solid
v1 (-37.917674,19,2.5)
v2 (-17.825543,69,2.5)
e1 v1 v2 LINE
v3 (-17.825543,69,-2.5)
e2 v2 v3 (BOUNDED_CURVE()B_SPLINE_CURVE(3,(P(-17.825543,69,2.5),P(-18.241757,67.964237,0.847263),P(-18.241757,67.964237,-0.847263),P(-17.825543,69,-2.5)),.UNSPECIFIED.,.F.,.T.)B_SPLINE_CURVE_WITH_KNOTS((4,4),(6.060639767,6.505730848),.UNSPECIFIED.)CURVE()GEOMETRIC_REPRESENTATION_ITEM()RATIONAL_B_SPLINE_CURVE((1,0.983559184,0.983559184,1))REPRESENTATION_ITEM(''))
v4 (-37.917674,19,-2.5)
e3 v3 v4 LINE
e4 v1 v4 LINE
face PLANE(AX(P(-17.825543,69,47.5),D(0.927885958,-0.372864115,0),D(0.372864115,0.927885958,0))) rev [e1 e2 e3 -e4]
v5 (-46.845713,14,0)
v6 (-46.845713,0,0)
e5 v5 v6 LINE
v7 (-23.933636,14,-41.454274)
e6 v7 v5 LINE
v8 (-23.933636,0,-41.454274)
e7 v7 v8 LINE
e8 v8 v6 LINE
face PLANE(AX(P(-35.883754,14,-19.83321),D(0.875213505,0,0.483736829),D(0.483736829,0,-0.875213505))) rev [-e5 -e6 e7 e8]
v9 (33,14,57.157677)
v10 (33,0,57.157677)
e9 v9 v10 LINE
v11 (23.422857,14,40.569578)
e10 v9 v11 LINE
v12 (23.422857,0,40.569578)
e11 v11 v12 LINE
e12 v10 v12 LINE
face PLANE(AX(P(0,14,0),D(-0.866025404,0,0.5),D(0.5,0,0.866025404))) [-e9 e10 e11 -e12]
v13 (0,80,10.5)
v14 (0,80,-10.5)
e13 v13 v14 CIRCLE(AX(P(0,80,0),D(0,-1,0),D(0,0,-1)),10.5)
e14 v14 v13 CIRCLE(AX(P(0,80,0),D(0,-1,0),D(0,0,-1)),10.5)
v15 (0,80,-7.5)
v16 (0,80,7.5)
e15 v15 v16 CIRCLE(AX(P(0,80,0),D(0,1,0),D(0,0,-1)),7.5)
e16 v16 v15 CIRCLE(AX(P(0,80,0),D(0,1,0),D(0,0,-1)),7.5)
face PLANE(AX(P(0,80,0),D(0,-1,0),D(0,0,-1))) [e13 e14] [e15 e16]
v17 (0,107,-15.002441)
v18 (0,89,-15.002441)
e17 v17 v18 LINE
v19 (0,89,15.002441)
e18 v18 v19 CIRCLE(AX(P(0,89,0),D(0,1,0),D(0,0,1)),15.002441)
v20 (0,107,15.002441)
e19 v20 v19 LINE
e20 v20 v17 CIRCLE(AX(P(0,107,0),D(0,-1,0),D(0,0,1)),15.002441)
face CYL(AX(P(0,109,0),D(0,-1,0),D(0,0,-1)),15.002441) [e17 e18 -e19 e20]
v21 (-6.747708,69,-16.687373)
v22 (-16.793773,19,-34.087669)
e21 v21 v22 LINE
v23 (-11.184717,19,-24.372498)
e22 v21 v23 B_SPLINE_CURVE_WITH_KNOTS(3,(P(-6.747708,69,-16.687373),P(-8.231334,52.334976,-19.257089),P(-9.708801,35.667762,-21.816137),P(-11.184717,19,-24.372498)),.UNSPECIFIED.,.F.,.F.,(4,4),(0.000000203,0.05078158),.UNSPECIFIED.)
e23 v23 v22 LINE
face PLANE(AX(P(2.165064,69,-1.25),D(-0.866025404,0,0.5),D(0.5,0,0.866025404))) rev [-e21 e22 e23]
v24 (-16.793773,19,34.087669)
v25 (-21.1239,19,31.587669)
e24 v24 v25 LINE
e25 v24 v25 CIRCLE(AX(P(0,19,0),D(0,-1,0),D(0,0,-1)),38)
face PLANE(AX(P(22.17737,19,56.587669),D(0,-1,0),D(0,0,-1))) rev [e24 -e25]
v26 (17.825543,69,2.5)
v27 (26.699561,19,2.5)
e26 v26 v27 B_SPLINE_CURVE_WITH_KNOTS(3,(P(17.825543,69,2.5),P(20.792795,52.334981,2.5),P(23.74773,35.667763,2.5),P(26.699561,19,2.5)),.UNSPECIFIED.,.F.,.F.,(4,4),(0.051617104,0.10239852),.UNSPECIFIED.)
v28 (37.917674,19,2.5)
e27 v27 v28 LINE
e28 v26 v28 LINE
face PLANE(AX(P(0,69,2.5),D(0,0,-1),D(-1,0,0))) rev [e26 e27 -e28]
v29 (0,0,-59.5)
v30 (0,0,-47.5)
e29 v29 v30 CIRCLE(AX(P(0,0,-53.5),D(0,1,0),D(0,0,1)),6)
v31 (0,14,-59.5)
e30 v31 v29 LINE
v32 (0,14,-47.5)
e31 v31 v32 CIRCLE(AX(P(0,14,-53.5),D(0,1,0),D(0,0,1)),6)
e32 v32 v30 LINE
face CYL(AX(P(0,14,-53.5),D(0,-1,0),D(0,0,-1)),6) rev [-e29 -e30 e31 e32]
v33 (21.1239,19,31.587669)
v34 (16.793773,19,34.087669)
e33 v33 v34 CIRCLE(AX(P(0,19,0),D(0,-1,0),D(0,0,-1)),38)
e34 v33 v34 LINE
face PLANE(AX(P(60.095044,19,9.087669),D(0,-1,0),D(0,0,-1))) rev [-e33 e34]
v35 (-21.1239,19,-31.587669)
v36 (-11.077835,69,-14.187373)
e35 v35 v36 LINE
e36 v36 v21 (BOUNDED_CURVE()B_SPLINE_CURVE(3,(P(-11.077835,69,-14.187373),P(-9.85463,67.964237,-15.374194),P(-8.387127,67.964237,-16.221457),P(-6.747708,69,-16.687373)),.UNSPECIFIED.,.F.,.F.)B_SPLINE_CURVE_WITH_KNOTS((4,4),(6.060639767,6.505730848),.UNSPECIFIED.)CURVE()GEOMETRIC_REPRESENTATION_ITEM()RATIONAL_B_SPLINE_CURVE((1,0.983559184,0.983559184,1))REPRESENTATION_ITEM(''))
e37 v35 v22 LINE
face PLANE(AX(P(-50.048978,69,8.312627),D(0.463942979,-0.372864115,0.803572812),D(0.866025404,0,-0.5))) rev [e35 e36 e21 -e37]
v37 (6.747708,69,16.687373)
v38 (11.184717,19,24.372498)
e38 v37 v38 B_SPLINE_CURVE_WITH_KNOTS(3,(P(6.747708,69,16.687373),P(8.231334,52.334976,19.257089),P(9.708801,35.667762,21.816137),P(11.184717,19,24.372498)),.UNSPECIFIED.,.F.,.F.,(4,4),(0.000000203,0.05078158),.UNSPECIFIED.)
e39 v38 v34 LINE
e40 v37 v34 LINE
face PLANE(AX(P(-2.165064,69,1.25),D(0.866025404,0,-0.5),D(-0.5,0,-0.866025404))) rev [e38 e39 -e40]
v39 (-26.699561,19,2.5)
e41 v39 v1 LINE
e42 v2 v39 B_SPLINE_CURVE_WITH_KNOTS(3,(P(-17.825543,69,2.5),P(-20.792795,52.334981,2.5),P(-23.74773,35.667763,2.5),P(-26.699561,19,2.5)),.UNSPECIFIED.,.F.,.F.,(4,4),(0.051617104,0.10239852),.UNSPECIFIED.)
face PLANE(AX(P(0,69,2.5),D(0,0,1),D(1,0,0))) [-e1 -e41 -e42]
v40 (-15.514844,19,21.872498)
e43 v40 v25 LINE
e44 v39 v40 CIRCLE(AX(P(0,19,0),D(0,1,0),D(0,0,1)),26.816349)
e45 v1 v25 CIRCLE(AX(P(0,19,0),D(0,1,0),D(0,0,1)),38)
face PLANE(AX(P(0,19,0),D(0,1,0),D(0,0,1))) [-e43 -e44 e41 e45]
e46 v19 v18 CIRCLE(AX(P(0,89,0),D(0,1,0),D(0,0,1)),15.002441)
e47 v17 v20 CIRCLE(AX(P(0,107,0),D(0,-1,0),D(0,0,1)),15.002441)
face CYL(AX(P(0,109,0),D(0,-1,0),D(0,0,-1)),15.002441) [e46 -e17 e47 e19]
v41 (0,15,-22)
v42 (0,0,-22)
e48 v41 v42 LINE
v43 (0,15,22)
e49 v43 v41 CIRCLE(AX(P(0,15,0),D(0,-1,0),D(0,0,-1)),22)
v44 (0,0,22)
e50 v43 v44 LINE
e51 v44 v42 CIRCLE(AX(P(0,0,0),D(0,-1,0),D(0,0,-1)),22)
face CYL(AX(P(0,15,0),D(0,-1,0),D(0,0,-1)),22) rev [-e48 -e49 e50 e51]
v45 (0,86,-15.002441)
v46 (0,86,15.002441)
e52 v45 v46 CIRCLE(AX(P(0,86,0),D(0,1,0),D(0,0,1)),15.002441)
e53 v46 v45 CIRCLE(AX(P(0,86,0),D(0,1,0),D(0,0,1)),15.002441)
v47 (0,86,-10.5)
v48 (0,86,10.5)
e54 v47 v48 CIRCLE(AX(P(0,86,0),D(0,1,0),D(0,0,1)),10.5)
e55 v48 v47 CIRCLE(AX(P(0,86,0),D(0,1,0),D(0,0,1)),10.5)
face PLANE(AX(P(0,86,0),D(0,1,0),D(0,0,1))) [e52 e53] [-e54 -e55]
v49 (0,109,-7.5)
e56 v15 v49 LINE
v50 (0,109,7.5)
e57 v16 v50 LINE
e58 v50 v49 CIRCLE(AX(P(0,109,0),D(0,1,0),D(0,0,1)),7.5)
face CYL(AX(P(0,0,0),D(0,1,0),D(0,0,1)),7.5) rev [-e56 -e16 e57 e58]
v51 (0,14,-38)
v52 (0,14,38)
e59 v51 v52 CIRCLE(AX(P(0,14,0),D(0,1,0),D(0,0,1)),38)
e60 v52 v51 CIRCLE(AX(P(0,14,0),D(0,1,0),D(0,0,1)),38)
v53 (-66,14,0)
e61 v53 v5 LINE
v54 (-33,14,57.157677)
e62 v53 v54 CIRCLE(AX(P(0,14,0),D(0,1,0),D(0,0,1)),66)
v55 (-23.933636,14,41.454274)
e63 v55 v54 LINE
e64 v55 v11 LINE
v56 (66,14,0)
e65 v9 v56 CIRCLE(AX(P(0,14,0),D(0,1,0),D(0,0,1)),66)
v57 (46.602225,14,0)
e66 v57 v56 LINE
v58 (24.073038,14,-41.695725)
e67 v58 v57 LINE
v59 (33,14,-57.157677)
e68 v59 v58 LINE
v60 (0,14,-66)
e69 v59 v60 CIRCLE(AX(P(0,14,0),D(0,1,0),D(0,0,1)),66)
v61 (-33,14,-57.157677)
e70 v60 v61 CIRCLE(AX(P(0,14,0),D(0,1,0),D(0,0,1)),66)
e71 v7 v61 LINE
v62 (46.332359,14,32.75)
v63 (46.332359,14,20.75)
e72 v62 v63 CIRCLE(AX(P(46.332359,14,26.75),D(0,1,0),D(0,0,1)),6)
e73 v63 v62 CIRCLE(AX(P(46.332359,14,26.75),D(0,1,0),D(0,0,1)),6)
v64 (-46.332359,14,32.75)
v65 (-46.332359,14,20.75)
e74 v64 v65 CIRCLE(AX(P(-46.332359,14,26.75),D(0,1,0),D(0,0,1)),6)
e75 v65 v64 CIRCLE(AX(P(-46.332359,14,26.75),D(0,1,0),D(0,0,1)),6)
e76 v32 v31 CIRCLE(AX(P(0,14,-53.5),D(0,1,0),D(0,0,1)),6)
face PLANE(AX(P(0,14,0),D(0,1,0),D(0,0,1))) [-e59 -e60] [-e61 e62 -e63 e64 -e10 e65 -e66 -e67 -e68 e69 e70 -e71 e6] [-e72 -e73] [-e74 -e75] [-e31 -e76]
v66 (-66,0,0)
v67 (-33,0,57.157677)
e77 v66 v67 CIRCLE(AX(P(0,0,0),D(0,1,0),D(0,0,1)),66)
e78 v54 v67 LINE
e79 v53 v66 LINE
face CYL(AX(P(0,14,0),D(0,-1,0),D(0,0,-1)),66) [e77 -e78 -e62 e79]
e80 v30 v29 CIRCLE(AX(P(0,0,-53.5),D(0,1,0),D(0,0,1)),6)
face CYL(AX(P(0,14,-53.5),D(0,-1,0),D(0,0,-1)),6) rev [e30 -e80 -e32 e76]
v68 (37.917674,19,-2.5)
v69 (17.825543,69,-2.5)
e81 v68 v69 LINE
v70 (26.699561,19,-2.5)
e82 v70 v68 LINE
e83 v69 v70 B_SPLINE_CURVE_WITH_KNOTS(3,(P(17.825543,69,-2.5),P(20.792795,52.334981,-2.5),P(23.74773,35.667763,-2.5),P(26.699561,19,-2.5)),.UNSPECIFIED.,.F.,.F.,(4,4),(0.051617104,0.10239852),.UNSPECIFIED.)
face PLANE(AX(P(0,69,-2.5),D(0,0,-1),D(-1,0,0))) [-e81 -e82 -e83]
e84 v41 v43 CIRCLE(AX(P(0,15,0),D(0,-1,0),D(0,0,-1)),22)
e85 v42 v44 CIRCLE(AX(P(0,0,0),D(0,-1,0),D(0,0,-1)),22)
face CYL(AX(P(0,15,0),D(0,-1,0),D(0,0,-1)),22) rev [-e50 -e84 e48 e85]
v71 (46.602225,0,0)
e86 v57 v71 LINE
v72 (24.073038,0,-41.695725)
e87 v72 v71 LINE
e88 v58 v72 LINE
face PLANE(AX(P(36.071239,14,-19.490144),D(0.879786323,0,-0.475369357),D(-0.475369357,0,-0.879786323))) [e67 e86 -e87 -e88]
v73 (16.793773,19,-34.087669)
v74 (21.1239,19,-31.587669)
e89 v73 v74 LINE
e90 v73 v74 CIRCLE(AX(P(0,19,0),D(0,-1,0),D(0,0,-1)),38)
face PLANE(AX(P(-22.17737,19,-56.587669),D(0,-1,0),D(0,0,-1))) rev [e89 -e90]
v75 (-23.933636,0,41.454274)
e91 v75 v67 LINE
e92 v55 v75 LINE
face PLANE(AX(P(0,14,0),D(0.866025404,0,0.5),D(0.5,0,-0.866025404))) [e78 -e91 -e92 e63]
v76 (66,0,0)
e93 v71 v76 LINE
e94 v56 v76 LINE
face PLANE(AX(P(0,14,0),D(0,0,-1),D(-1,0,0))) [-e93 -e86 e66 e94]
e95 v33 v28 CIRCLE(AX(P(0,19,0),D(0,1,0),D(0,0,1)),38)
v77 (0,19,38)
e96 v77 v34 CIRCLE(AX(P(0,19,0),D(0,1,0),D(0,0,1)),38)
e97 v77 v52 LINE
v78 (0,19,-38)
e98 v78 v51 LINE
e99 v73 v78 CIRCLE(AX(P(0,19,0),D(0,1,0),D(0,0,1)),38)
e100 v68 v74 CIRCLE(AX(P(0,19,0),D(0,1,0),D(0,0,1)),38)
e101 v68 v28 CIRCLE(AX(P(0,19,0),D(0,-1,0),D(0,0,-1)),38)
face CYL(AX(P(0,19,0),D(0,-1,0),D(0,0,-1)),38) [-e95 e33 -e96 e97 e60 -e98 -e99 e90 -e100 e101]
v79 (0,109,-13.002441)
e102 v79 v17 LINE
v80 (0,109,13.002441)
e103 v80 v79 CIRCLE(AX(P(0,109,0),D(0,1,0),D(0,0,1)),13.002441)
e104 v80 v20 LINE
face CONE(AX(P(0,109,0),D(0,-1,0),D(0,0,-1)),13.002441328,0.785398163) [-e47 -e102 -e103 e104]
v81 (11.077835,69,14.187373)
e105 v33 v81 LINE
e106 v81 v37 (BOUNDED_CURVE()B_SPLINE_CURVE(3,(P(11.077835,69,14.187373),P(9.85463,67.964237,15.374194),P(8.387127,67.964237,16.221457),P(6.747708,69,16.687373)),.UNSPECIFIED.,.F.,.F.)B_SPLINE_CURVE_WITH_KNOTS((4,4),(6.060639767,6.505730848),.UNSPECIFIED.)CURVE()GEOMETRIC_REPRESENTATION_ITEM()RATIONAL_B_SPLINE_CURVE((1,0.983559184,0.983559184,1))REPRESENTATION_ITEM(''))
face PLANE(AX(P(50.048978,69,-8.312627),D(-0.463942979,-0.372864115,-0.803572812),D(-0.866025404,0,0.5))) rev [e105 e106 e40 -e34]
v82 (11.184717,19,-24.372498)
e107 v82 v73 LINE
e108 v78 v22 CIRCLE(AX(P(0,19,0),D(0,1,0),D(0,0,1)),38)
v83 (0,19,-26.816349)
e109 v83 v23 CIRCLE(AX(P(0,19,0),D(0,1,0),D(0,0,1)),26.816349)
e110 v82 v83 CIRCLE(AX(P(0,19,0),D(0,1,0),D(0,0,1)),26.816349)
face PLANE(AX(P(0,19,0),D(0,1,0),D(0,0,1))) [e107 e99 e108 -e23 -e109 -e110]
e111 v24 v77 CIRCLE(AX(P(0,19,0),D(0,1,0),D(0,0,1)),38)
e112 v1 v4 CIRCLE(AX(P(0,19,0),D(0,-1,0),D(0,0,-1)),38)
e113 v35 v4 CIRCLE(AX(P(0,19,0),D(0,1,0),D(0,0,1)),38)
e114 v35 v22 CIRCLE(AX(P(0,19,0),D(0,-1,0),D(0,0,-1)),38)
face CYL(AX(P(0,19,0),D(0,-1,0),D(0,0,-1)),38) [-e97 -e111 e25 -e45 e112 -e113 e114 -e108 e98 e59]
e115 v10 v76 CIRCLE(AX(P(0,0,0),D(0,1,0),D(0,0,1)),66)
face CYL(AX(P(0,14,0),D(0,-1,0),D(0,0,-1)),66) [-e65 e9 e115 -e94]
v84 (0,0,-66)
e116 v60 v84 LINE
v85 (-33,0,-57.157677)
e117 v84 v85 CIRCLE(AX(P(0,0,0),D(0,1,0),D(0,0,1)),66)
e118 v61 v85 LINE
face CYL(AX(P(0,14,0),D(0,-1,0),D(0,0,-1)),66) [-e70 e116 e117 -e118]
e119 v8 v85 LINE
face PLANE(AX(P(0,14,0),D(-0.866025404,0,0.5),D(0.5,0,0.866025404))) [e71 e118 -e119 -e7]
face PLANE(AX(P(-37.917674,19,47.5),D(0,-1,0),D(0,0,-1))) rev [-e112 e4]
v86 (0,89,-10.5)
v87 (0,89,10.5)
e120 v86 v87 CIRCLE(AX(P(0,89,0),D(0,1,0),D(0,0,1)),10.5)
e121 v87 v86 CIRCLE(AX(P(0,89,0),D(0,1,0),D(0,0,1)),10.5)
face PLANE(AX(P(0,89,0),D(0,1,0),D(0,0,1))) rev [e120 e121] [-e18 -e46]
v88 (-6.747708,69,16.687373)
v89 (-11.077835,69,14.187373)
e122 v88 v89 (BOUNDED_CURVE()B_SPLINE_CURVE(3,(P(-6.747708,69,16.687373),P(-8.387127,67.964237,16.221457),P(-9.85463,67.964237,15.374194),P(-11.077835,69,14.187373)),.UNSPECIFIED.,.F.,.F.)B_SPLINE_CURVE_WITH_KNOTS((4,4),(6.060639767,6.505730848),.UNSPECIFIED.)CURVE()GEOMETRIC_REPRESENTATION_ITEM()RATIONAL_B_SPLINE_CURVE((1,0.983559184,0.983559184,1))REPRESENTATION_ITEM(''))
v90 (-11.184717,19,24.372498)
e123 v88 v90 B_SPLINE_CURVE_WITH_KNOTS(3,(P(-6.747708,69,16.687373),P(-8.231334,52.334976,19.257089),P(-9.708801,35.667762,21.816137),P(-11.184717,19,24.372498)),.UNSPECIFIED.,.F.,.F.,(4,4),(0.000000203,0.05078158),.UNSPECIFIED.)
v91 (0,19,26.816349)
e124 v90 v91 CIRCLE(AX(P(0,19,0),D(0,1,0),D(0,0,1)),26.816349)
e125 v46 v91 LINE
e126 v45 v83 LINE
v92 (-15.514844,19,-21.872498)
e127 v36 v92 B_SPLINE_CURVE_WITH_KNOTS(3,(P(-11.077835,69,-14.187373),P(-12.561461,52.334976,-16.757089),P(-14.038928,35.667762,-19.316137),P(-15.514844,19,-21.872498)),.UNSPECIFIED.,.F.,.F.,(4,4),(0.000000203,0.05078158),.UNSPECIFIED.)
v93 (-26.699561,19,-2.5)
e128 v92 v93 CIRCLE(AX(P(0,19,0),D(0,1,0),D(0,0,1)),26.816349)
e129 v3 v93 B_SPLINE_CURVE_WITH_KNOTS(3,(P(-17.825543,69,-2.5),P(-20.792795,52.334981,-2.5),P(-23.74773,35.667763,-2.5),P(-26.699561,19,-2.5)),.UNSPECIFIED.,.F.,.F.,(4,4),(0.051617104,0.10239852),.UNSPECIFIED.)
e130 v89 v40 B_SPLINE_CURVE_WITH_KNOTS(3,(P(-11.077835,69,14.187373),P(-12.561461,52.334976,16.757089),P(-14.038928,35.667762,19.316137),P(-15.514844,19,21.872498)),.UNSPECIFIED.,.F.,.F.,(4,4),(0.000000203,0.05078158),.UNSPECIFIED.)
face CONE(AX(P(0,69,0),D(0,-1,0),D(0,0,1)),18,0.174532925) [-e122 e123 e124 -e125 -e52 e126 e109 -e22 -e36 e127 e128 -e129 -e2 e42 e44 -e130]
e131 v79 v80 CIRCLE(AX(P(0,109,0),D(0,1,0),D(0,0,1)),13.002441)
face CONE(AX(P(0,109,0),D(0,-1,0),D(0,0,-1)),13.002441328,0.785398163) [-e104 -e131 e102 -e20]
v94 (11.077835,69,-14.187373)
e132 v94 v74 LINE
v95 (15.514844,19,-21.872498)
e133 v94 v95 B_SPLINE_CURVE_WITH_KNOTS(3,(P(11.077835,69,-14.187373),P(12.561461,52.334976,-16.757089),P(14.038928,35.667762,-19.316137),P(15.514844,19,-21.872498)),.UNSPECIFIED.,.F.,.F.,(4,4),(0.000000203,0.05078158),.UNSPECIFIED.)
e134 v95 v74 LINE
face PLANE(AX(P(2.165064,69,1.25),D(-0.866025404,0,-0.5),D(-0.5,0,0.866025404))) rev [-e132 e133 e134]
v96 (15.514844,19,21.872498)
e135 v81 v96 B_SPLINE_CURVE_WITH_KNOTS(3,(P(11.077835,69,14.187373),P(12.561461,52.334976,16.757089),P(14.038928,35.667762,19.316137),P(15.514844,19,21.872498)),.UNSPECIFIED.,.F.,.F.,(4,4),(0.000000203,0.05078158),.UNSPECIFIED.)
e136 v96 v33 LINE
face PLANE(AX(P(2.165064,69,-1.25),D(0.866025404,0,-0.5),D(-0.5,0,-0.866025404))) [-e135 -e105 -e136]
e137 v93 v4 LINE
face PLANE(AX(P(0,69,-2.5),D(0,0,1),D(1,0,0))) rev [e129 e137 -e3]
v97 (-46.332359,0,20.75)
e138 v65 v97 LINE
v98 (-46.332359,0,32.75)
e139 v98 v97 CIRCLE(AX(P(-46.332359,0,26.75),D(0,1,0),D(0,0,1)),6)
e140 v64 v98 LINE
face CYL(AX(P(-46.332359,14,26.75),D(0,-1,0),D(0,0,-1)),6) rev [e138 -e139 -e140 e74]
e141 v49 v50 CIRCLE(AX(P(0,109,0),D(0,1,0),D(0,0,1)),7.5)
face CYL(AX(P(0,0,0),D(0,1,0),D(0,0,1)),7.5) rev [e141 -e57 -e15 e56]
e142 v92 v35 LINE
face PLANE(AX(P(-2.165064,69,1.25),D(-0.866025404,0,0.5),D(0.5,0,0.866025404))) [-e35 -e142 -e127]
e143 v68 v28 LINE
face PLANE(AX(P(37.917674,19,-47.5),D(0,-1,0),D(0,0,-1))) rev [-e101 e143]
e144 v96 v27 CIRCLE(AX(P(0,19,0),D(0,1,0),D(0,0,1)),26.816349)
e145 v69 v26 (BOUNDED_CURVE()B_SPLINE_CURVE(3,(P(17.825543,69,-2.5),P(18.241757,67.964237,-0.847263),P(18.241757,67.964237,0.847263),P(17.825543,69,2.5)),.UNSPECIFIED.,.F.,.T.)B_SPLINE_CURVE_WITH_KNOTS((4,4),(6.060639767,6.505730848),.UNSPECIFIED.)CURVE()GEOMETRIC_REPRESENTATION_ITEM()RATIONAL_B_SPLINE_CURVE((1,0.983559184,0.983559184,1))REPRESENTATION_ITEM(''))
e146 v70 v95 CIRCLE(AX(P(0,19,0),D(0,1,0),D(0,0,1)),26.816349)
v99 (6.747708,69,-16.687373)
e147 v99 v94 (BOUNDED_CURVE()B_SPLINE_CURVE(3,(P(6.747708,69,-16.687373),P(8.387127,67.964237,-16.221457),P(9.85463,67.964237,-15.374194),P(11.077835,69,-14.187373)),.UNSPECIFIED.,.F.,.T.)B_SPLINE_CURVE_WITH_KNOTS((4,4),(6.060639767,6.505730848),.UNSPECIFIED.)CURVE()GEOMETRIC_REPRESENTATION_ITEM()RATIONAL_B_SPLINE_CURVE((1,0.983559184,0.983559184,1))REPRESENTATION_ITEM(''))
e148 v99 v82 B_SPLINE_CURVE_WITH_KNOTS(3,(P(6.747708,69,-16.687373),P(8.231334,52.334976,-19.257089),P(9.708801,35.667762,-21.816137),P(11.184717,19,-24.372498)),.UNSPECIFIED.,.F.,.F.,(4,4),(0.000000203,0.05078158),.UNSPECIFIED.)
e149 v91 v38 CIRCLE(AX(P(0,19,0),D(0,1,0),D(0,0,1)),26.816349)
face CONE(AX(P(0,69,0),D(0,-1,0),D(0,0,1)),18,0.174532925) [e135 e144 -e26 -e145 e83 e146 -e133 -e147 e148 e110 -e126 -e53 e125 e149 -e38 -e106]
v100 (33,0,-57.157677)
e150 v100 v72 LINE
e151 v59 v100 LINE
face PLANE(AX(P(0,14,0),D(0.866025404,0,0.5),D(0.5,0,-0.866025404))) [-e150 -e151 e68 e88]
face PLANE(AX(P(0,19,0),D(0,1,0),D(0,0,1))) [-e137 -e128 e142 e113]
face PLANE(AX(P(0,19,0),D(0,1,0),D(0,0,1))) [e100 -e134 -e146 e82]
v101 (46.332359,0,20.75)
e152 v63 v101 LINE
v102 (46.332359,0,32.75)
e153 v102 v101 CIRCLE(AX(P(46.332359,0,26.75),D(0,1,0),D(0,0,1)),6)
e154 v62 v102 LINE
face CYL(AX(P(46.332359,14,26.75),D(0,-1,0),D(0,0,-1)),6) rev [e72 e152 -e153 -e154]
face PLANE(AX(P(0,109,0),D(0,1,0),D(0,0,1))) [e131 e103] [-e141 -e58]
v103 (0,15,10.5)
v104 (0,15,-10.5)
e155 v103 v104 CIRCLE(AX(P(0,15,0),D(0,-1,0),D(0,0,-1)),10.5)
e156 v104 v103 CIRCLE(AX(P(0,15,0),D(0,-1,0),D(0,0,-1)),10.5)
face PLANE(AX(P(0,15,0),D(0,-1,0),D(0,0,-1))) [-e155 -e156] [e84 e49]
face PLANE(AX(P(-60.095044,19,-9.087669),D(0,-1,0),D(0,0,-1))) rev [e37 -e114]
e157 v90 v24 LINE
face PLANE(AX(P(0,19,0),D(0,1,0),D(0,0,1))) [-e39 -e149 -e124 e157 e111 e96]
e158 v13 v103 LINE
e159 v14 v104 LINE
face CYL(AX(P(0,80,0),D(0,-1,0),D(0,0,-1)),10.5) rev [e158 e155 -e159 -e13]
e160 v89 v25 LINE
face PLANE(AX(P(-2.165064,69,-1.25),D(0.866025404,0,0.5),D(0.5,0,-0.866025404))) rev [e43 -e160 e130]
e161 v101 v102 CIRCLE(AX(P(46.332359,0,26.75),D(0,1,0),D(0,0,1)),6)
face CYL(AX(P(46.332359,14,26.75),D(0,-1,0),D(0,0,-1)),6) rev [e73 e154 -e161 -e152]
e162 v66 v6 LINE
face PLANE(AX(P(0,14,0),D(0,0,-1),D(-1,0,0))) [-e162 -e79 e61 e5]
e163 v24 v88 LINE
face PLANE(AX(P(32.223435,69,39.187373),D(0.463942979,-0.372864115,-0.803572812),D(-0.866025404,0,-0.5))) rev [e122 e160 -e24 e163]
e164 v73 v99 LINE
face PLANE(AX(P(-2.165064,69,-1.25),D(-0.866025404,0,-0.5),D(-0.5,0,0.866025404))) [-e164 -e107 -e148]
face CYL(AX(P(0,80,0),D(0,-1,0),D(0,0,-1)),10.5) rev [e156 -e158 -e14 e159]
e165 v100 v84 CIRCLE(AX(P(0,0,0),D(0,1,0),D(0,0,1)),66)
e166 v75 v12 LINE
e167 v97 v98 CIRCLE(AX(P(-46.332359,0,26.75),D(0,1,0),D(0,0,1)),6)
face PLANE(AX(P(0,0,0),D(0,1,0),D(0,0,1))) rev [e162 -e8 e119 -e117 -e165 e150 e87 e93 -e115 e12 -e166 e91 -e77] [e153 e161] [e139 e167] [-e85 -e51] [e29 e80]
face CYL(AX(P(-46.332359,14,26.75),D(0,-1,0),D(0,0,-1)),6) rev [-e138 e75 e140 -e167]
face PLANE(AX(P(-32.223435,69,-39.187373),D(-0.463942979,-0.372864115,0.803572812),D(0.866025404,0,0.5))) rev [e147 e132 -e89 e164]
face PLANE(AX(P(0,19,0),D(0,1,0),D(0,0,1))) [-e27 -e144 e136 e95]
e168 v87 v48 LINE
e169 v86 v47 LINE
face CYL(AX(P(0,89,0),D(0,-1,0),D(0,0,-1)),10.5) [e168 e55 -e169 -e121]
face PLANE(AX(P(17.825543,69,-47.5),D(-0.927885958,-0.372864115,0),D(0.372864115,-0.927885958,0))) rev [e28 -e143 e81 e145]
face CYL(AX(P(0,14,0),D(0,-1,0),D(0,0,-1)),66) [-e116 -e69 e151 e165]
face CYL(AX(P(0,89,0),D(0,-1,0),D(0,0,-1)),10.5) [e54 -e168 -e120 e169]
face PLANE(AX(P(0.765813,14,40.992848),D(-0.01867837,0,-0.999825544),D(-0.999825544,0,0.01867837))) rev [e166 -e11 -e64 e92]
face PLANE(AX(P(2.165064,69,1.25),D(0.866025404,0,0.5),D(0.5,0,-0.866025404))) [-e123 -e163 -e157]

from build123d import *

# Parameters (mm, degrees)
BASE_FLANGE_SKETCH_R             = 6
F_3_LOBE_BASE_FLANGE_DEPTH       = 14
LOCATING_COLLAR_SKETCH_R         = 38
LOCATING_COLLAR_76_DEPTH         = 5
RIB_WEB_DEPTH                    = 50
RIB_SLOT_CUT_1_DEPTH             = 50
RIB_SLOT_CUT_2_DEPTH             = 50
RIB_SLOT_CUT_3_DEPTH             = 50
RIB_SLOT_CUT_4_DEPTH             = 50
RIB_SLOT_CUT_5_DEPTH             = 50
RIB_SLOT_CUT_6_DEPTH             = 50
CONE_BASE_SKETCH_36_R            = 18
CONICAL_COLUMN_10DEG_DRAFT_DEPTH = 17
CONICAL_COLUMN_10DEG_DRAFT_TAPER = 10
SKETCH10_2_R                     = 18
CONE_CORE_THROUGH_RIBS_DEPTH     = 50
CONE_CORE_THROUGH_RIBS_DRAFT     = 10
NECK_SKETCH_R                    = 10.5
NECK_21_DEPTH                    = 3
TOP_SPIGOT_SKETCH_R              = 15.002441328
TOP_SPIGOT_30_DEPTH              = 20
SPIGOT_CHAMFER_2MM_SIZE          = 2
THROUGH_BORE_SKETCH_R            = 7.5
THROUGH_BORE_15_DEPTH            = 144.502613217
UNDERSIDE_COUNTERBORE_SKETCH_R   = 22
UNDERSIDE_COUNTERBORE_44_DEPTH   = 15
INNER_BORE_SKETCH_R              = 10.5
INNER_BORE_21_DEPTH              = 65


with BuildPart() as part:
    # Base Flange Sketch → 3-Lobe Base Flange (new body)
    with BuildSketch(Plane(origin=(0, 0, 0), x_dir=(1, 0, 0), z_dir=(0, 1, 0))):
        with BuildLine():
            Line((33, -57.15767665), (23.422856537, -40.56957758))
            Line((23.422856537, -40.56957758), (-23.933636252, -41.454273999))
            Line((-23.933636252, -41.454273999), (-33, -57.15767665))
            ThreePointArc((-33, -57.15767665), (-57.15767665, -33), (-66, 0))
            Line((-66, 0), (-46.845713073, 0))
            Line((-46.845713073, 0), (-23.933636252, 41.454273999))
            Line((-23.933636252, 41.454273999), (-33, 57.15767665))
            ThreePointArc((-33, 57.15767665), (0, 66), (33, 57.15767665))
            Line((33, 57.15767665), (24.073038277, 41.695725388))
            Line((24.073038277, 41.695725388), (46.60222479, 0))
            Line((46.60222479, 0), (66, 0))
            ThreePointArc((66, 0), (57.15767665, -33), (33, -57.15767665))
        make_face()
        with Locations(Location((0, 53.5, 0), (0, 0, 270))):
            Circle(BASE_FLANGE_SKETCH_R, mode=Mode.SUBTRACT)
        with Locations(Location((46.332359102, -26.75, 0), (0, 0, 270))):
            Circle(BASE_FLANGE_SKETCH_R, mode=Mode.SUBTRACT)
        with Locations(Location((-46.332359102, -26.75, 0), (0, 0, 270))):
            Circle(BASE_FLANGE_SKETCH_R, mode=Mode.SUBTRACT)
    extrude(amount=F_3_LOBE_BASE_FLANGE_DEPTH)

    # Locating Collar Sketch → Locating Collar _76 (add)
    with BuildSketch(Plane(origin=(0, 14, 0), x_dir=(1, 0, 0), z_dir=(0, 1, 0))):
        with Locations(Location((0, 0, 0), (0, 0, 270))):
            Circle(LOCATING_COLLAR_SKETCH_R)
    extrude(amount=LOCATING_COLLAR_76_DEPTH)

    # Rib Web Sketch → Rib Web (add)
    with BuildSketch(Plane(origin=(0, 19, 0), x_dir=(1, 0, 0), z_dir=(0, 1, 0))):
        with BuildLine():
            Line((37.917673979, 2.5), (17.82554347, 2.5))
            ThreePointArc((17.82554347, 2.5), (15.588457268, 9), (11.077835244, 14.187373481))
            Line((11.077835244, 14.187373481), (21.123900499, 31.587668918))
            ThreePointArc((21.123900499, 31.587668918), (19, 32.908965344), (16.79377348, 34.087668918))
            Line((16.79377348, 34.087668918), (6.747708226, 16.687373481))
            ThreePointArc((6.747708226, 16.687373481), (0, 18), (-6.747708226, 16.687373481))
            Line((-6.747708226, 16.687373481), (-16.79377348, 34.087668918))
            ThreePointArc((-16.79377348, 34.087668918), (-19, 32.908965344), (-21.123900499, 31.587668918))
            Line((-21.123900499, 31.587668918), (-11.077835244, 14.187373481))
            ThreePointArc((-11.077835244, 14.187373481), (-15.588457268, 9), (-17.82554347, 2.5))
            Line((-17.82554347, 2.5), (-37.917673979, 2.5))
            ThreePointArc((-37.917673979, 2.5), (-38, 0), (-37.917673979, -2.5))
            Line((-37.917673979, -2.5), (-17.82554347, -2.5))
            ThreePointArc((-17.82554347, -2.5), (-15.588457268, -9), (-11.077835244, -14.187373481))
            Line((-11.077835244, -14.187373481), (-21.123900499, -31.587668918))
            ThreePointArc((-21.123900499, -31.587668918), (-19, -32.908965344), (-16.79377348, -34.087668918))
            Line((-16.79377348, -34.087668918), (-6.747708226, -16.687373481))
            ThreePointArc((-6.747708226, -16.687373481), (0, -18), (6.747708226, -16.687373481))
            Line((6.747708226, -16.687373481), (16.79377348, -34.087668918))
            ThreePointArc((16.79377348, -34.087668918), (19, -32.908965344), (21.123900499, -31.587668918))
            Line((21.123900499, -31.587668918), (11.077835244, -14.187373481))
            ThreePointArc((11.077835244, -14.187373481), (15.588457268, -9), (17.82554347, -2.5))
            Line((17.82554347, -2.5), (37.917673979, -2.5))
            ThreePointArc((37.917673979, -2.5), (37.979412918, -1.250677574), (38, 0))
            ThreePointArc((38, 0), (37.979412918, 1.250677574), (37.917673979, 2.5))
        make_face()
    extrude(amount=RIB_WEB_DEPTH)

    # Rib Slot 1 Sketch → Rib Slot Cut 1 (cut)
    with BuildSketch(Plane(origin=(-2.165063509, 0, 1.25), x_dir=(0.5000000000000031, 0, 0.8660254037844369), z_dir=(-0.8660254037844369, 0, 0.5000000000000031))):
        Polygon((17.82554347, 69), (37.917673979, 19), (44.908281954, 19), (44.908281954, 71.637843916), align=None)
    extrude(amount=-RIB_SLOT_CUT_1_DEPTH, mode=Mode.SUBTRACT)

    # Rib Slot 2 Sketch → Rib Slot Cut 2 (cut)
    with BuildSketch(Plane.XY.offset(2.5)):
        Polygon((37.917673979, 19), (41.484682242, 19), (43.003646089, 71.350074734), (17.82554347, 69), align=None)
    extrude(amount=-RIB_SLOT_CUT_2_DEPTH, mode=Mode.SUBTRACT)

    # Rib Slot 3 Sketch → Rib Slot Cut 3 (cut)
    with BuildSketch(Plane(origin=(2.165063509, 0, 1.25), x_dir=(0.49999999999999784, 0, -0.86602540378444), z_dir=(0.86602540378444, 0, 0.49999999999999784))):
        Polygon((17.82554347, 69), (37.917673979, 19), (41.057228015, 19), (41.057228015, 71.20053138), align=None)
    extrude(amount=-RIB_SLOT_CUT_3_DEPTH, mode=Mode.SUBTRACT)

    # Rib Slot 4 Sketch → Rib Slot Cut 4 (cut)
    with BuildSketch(Plane(origin=(2.165063509, 0, -1.25), x_dir=(-0.5000000000000029, 0, -0.866025403784437), z_dir=(0.866025403784437, 0, -0.5000000000000029))):
        Polygon((17.82554347, 69), (37.917673979, 19), (43.490166386, 19), (43.490166386, 73.364655625), align=None)
    extrude(amount=-RIB_SLOT_CUT_4_DEPTH, mode=Mode.SUBTRACT)

    # Rib Slot 5 Sketch → Rib Slot Cut 5 (cut)
    with BuildSketch(Plane(origin=(0, 0, -2.5), x_dir=(-1, 0, 0), z_dir=(0, 0, -1))):
        Polygon((17.82554347, 69), (37.917673979, 19), (42.214088477, 19), (42.214088477, 71.586453607), align=None)
    extrude(amount=-RIB_SLOT_CUT_5_DEPTH, mode=Mode.SUBTRACT)

    # Rib Slot 6 Sketch → Rib Slot Cut 6 (cut)
    with BuildSketch(Plane(origin=(-2.165063509, 0, -1.25), x_dir=(-0.4999999999999972, 0, 0.8660254037844403), z_dir=(-0.8660254037844403, 0, -0.4999999999999972))):
        Polygon((17.82554347, 69), (37.917673979, 19), (44.978143034, 19), (44.978143034, 73.134659176), align=None)
    extrude(amount=-RIB_SLOT_CUT_6_DEPTH, mode=Mode.SUBTRACT)

    # Cone Base Sketch _36 → Conical Column 10deg Draft (add)
    with BuildSketch(Plane(origin=(0, 69, 0), x_dir=(1, 0, 0), z_dir=(0, 1, 0))):
        Circle(CONE_BASE_SKETCH_36_R)
    extrude(amount=CONICAL_COLUMN_10DEG_DRAFT_DEPTH, taper=CONICAL_COLUMN_10DEG_DRAFT_TAPER)


with BuildPart() as cone_core_through_ribs_tool:
    # Sketch10_2 → Cone Core Through Ribs (with draft: the straight prism first)
    with BuildSketch(Plane(origin=(0, 69, 0), x_dir=(1, 0, 0), z_dir=(0, 1, 0))):
        Circle(SKETCH10_2_R)
    extrude(amount=-CONE_CORE_THROUGH_RIBS_DEPTH)
    # Cone Core Through Ribs: the draft: its side faces are tilted about the plane it starts from
    cone_core_through_ribs_sides = [cone_core_through_ribs_tool.faces().sort_by_distance(p)[0] for p in [
        (-18, 44, 0),
    ]]
    draft(cone_core_through_ribs_sides, Plane(origin=(0, 69, 0), x_dir=(1, 0, 0), z_dir=(0, 1, 0)), CONE_CORE_THROUGH_RIBS_DRAFT)


with BuildPart() as part_1:
    add(part.part)

    # Cone Core Through Ribs: add cone_core_through_ribs_tool
    add(cone_core_through_ribs_tool.part)

    # Neck Sketch → Neck _21 (add)
    with BuildSketch(Plane(origin=(0, 86, 0), x_dir=(1, 0, 0), z_dir=(0, 1, 0))):
        with Locations(Location((0, 0, 0), (0, 0, 270))):
            Circle(NECK_SKETCH_R)
    extrude(amount=NECK_21_DEPTH)

    # Top Spigot Sketch → Top Spigot _30 (add)
    with BuildSketch(Plane(origin=(0, 89, 0), x_dir=(1, 0, 0), z_dir=(0, 1, 0))):
        with Locations(Location((0, 0, 0), (0, 0, 270))):
            Circle(TOP_SPIGOT_SKETCH_R)
    extrude(amount=TOP_SPIGOT_30_DEPTH)

    # Spigot Chamfer 2mm
    spigot_chamfer_2mm_edges = [part_1.edges().sort_by_distance(p)[0] for p in [
        (0, 109, -15.002441328),
    ]]
    chamfer(spigot_chamfer_2mm_edges, length=SPIGOT_CHAMFER_2MM_SIZE)

    # Through Bore Sketch → Through Bore _15 (cut, through all)
    with BuildSketch(Plane(origin=(0, 109, 0), x_dir=(1, 0, 0), z_dir=(0, 1, 0))):
        with Locations(Location((0, 0, 0), (0, 0, 270))):
            Circle(THROUGH_BORE_SKETCH_R)
    extrude(amount=-THROUGH_BORE_15_DEPTH, mode=Mode.SUBTRACT)

    # Underside Counterbore Sketch → Underside Counterbore _44 (cut)
    with BuildSketch(Plane.XZ):
        with Locations(Location((0, 0, 0), (0, 0, 270))):
            Circle(UNDERSIDE_COUNTERBORE_SKETCH_R)
    extrude(amount=-UNDERSIDE_COUNTERBORE_44_DEPTH, mode=Mode.SUBTRACT)

    # Inner Bore Sketch → Inner Bore _21 (cut)
    with BuildSketch(Plane.XZ.offset(-15)):
        with Locations(Location((0, 0, 0), (0, 0, 90))):
            Circle(INNER_BORE_SKETCH_R)
    extrude(amount=-INNER_BORE_21_DEPTH, mode=Mode.SUBTRACT)


solid = part_1.part
